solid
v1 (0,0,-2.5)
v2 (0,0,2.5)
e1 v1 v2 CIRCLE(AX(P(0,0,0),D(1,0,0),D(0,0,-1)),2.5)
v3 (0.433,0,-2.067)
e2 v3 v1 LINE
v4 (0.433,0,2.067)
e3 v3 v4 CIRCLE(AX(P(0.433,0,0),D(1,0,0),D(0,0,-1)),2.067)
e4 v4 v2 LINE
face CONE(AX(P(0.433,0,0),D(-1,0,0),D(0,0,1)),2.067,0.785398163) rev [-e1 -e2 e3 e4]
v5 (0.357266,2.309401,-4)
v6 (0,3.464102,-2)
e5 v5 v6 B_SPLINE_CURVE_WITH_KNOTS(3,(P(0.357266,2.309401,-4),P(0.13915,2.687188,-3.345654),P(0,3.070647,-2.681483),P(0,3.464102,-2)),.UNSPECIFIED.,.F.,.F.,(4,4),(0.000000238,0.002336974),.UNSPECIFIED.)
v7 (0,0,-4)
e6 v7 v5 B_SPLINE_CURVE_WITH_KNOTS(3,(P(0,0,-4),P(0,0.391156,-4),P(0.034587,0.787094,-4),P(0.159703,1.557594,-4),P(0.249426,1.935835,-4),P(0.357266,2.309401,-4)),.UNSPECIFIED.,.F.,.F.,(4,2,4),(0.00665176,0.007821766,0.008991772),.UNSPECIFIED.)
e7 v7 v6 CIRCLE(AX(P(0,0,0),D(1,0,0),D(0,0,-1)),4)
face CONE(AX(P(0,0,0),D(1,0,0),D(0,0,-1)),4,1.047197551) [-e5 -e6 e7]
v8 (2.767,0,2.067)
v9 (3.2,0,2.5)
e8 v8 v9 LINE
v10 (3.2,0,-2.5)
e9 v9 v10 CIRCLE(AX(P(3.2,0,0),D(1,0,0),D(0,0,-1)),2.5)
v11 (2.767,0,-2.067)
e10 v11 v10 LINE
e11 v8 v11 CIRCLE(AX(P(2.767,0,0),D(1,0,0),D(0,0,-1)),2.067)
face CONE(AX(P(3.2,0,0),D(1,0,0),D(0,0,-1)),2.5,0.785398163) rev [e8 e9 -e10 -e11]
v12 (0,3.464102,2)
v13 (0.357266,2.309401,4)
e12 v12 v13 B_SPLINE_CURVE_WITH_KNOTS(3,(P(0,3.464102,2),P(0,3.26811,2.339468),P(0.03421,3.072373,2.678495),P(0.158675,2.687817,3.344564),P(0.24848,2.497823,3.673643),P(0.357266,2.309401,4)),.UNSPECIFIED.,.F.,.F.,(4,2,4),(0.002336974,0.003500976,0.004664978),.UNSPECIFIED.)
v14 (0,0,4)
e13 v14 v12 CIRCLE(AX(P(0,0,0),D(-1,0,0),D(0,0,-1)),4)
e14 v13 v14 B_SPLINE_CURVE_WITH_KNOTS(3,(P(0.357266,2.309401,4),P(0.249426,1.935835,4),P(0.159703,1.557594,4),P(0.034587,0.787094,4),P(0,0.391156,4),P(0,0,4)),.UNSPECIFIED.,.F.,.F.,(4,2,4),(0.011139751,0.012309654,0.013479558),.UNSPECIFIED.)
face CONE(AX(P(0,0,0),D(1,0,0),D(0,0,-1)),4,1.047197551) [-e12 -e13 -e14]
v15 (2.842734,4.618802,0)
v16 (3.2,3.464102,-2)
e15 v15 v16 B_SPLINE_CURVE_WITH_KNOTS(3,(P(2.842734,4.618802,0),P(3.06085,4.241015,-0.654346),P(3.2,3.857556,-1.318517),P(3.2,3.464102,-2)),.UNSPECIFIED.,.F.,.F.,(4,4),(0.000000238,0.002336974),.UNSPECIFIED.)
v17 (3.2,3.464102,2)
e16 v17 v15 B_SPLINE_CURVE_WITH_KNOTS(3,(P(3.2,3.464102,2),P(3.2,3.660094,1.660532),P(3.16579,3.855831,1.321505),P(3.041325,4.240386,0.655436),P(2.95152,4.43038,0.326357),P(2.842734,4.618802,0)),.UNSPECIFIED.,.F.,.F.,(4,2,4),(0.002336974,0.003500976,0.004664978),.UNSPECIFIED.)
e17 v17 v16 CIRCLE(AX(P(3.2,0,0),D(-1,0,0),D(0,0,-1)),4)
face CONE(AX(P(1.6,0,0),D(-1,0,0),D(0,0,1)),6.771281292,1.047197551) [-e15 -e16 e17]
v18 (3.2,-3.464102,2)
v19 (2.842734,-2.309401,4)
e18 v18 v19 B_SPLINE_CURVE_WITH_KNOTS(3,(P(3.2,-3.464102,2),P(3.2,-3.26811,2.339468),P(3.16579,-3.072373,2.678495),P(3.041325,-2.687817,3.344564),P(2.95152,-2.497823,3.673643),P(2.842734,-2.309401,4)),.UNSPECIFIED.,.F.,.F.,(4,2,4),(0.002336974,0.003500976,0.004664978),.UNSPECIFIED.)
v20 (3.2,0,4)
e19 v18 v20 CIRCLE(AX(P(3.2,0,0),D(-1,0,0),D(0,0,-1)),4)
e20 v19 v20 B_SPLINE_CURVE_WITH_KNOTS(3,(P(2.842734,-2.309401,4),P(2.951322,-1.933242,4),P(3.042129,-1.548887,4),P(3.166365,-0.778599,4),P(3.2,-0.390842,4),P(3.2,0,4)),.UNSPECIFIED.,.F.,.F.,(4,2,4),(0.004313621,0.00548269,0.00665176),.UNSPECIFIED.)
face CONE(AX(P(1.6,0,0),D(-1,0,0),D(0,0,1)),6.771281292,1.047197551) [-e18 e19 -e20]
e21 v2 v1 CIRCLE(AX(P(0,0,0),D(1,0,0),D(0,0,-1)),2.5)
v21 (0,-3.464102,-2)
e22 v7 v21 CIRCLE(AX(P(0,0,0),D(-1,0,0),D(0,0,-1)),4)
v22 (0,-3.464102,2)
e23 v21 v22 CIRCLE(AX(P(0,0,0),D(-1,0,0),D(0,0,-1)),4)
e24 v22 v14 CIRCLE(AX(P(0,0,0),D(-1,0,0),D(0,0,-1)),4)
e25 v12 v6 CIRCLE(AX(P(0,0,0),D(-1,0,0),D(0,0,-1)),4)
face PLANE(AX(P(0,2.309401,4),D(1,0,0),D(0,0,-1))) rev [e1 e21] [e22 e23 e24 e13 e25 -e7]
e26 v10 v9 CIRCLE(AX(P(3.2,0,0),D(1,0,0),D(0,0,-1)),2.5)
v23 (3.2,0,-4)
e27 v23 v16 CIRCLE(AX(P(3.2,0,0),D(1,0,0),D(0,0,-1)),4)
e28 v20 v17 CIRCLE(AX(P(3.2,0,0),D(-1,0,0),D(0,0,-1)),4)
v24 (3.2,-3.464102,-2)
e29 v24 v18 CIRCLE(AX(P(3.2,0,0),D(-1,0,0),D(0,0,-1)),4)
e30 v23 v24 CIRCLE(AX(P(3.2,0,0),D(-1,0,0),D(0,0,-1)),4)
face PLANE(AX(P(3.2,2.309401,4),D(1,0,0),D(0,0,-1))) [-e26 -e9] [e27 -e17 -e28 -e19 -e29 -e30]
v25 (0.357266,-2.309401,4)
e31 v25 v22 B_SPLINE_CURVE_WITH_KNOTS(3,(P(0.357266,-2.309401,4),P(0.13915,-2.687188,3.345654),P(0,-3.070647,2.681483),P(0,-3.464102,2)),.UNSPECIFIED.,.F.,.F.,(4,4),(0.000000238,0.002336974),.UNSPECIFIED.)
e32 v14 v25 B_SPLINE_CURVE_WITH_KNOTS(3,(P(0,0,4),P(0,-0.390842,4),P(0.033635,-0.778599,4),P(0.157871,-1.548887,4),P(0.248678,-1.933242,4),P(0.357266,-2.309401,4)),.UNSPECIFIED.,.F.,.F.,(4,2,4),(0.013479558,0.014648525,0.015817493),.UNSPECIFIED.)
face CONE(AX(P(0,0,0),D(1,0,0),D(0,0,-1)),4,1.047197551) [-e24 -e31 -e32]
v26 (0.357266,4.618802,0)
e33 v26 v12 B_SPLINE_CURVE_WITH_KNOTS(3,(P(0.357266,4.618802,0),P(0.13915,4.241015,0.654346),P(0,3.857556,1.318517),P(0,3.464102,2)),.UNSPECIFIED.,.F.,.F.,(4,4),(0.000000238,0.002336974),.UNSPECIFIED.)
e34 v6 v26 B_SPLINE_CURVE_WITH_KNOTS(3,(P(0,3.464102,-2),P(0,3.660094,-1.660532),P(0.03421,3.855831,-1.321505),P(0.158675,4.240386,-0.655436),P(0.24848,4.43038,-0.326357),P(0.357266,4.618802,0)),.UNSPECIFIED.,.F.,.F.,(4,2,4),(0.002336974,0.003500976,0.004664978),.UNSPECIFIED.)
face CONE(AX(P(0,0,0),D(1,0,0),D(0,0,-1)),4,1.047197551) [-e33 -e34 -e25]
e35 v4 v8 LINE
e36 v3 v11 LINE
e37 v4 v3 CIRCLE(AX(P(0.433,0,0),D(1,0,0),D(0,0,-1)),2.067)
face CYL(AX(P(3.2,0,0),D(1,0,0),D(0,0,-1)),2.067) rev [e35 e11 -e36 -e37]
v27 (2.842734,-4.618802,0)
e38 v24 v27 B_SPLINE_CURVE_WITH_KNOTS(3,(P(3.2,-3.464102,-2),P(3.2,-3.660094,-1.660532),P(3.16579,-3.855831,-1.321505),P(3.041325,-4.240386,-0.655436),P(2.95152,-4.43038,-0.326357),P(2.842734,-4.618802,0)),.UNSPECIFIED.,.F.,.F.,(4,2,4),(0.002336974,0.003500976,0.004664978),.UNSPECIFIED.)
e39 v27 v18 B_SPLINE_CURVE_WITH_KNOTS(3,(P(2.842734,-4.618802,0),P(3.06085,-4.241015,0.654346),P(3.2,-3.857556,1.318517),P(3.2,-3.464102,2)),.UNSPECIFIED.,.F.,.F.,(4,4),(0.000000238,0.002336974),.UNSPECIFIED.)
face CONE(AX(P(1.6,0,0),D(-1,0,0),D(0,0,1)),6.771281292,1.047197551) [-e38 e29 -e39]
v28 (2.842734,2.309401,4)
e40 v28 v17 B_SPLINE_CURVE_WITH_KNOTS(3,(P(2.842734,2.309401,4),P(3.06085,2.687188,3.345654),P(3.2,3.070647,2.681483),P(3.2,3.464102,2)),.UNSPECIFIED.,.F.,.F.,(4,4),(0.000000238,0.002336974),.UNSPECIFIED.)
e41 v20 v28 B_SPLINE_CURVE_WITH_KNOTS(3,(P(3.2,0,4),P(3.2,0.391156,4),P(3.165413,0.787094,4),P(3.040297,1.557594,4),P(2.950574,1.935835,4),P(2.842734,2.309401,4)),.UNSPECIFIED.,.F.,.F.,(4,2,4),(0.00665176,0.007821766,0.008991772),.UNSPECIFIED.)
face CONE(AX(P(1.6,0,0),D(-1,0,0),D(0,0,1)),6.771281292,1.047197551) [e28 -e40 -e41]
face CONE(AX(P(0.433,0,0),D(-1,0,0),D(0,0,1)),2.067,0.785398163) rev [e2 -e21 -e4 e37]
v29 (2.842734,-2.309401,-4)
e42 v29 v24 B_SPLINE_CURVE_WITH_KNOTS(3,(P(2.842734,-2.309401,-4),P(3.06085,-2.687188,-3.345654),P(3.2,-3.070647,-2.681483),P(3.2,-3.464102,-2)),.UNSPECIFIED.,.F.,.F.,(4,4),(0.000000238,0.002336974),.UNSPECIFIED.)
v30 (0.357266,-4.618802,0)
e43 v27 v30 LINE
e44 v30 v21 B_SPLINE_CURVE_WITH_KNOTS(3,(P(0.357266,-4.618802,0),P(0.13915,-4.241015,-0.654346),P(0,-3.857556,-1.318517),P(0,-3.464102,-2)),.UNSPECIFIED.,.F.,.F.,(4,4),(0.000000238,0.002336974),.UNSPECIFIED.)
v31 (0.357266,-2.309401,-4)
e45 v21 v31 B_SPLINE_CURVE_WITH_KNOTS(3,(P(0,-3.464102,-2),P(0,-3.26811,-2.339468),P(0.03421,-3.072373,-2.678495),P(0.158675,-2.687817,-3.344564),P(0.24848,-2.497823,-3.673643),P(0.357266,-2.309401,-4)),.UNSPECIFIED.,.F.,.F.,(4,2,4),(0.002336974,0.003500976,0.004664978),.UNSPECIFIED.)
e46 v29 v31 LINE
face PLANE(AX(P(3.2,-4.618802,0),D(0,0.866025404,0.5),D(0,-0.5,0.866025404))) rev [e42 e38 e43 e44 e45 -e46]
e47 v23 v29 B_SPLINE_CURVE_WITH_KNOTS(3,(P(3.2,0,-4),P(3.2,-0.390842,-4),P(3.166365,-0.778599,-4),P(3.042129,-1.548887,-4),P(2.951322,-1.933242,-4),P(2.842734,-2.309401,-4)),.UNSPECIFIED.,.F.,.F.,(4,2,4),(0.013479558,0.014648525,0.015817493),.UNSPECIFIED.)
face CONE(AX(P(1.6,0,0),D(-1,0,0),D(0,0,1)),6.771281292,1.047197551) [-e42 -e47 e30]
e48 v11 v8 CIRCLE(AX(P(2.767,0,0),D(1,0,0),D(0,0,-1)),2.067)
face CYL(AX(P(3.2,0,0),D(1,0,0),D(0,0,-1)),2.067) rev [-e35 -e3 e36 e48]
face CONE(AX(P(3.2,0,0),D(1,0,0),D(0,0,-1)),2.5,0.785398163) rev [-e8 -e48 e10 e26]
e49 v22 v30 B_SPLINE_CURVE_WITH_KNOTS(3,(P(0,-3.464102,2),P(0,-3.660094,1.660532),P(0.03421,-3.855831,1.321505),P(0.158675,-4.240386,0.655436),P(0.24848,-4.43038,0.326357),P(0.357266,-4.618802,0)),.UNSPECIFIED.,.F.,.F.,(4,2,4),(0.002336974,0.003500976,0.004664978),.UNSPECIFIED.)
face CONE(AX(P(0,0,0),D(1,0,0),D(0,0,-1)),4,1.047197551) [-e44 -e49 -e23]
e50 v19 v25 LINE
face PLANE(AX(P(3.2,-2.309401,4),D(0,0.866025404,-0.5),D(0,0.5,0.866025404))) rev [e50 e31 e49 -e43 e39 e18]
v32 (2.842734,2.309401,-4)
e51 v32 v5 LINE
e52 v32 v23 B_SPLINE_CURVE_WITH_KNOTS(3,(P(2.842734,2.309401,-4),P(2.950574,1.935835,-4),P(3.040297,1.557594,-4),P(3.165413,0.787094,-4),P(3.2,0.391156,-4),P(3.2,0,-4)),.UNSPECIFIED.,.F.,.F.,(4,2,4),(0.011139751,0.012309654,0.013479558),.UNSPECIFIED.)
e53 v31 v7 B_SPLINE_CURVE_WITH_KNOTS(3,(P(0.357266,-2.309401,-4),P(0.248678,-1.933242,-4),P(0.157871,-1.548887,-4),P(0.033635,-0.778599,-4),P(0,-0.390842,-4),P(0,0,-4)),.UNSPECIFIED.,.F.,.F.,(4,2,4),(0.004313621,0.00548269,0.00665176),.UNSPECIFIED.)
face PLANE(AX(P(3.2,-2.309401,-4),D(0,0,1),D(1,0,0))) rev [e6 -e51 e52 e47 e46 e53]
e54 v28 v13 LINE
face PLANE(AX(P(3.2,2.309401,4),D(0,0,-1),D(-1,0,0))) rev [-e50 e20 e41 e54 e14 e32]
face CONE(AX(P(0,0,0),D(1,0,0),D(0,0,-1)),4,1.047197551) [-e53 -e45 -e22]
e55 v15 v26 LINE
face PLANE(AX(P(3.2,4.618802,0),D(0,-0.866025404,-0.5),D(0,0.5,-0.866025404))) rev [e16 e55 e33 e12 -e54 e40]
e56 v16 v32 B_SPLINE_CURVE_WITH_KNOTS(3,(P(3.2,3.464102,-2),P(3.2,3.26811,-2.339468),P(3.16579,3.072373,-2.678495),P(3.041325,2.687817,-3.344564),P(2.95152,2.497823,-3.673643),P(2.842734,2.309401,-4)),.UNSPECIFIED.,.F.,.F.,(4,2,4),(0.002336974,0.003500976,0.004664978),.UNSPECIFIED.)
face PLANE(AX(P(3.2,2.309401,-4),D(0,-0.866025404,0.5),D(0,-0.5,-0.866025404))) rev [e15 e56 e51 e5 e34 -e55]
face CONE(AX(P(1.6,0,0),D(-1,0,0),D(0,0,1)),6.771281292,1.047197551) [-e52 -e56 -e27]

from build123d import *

# Parameters (mm, degrees)
BOSS_EXTRUDE1_DEPTH = 3.2


with BuildPart() as part:
    # Sketch1 → Boss-Extrude1 (new body)
    with BuildSketch(Plane(origin=(0, 0, 0), x_dir=(0, 0, -1), z_dir=(1, 0, 0))):
        Polygon((-4, 2.309401077), (-4, -2.309401077), (0, -4.618802154), (4, -2.309401077), (4, 2.309401077), (0, 4.618802154), align=None)
    extrude(amount=BOSS_EXTRUDE1_DEPTH)

    # Sketch2 → Cut-Revolve1 (revolve, cut)
    with BuildSketch(Plane.XY):
        Polygon((0, 4), (1.6, 6.771281292), (3.2, 4), (3.2, 10.2), (0, 10.2), align=None)
    revolve(axis=Axis((50, 0, 0), (-1, 0, 0)), mode=Mode.SUBTRACT)

    # Sketch3 → Cut-Revolve2 (revolve, cut)
    with BuildSketch(Plane.XY, mode=Mode.PRIVATE) as cut_revolve2_sk:
        Polygon((0, 0), (0, 2.5), (0.433, 2.067), (2.767, 2.067), (3.2, 2.5), (3.2, 0), align=None)
    revolve(cut_revolve2_sk.sketch.rotate(Axis((3.2, 0, 0), (-1, 0, 0)), 90), axis=Axis((3.2, 0, 0), (-1, 0, 0)), mode=Mode.SUBTRACT)


solid = part.part
